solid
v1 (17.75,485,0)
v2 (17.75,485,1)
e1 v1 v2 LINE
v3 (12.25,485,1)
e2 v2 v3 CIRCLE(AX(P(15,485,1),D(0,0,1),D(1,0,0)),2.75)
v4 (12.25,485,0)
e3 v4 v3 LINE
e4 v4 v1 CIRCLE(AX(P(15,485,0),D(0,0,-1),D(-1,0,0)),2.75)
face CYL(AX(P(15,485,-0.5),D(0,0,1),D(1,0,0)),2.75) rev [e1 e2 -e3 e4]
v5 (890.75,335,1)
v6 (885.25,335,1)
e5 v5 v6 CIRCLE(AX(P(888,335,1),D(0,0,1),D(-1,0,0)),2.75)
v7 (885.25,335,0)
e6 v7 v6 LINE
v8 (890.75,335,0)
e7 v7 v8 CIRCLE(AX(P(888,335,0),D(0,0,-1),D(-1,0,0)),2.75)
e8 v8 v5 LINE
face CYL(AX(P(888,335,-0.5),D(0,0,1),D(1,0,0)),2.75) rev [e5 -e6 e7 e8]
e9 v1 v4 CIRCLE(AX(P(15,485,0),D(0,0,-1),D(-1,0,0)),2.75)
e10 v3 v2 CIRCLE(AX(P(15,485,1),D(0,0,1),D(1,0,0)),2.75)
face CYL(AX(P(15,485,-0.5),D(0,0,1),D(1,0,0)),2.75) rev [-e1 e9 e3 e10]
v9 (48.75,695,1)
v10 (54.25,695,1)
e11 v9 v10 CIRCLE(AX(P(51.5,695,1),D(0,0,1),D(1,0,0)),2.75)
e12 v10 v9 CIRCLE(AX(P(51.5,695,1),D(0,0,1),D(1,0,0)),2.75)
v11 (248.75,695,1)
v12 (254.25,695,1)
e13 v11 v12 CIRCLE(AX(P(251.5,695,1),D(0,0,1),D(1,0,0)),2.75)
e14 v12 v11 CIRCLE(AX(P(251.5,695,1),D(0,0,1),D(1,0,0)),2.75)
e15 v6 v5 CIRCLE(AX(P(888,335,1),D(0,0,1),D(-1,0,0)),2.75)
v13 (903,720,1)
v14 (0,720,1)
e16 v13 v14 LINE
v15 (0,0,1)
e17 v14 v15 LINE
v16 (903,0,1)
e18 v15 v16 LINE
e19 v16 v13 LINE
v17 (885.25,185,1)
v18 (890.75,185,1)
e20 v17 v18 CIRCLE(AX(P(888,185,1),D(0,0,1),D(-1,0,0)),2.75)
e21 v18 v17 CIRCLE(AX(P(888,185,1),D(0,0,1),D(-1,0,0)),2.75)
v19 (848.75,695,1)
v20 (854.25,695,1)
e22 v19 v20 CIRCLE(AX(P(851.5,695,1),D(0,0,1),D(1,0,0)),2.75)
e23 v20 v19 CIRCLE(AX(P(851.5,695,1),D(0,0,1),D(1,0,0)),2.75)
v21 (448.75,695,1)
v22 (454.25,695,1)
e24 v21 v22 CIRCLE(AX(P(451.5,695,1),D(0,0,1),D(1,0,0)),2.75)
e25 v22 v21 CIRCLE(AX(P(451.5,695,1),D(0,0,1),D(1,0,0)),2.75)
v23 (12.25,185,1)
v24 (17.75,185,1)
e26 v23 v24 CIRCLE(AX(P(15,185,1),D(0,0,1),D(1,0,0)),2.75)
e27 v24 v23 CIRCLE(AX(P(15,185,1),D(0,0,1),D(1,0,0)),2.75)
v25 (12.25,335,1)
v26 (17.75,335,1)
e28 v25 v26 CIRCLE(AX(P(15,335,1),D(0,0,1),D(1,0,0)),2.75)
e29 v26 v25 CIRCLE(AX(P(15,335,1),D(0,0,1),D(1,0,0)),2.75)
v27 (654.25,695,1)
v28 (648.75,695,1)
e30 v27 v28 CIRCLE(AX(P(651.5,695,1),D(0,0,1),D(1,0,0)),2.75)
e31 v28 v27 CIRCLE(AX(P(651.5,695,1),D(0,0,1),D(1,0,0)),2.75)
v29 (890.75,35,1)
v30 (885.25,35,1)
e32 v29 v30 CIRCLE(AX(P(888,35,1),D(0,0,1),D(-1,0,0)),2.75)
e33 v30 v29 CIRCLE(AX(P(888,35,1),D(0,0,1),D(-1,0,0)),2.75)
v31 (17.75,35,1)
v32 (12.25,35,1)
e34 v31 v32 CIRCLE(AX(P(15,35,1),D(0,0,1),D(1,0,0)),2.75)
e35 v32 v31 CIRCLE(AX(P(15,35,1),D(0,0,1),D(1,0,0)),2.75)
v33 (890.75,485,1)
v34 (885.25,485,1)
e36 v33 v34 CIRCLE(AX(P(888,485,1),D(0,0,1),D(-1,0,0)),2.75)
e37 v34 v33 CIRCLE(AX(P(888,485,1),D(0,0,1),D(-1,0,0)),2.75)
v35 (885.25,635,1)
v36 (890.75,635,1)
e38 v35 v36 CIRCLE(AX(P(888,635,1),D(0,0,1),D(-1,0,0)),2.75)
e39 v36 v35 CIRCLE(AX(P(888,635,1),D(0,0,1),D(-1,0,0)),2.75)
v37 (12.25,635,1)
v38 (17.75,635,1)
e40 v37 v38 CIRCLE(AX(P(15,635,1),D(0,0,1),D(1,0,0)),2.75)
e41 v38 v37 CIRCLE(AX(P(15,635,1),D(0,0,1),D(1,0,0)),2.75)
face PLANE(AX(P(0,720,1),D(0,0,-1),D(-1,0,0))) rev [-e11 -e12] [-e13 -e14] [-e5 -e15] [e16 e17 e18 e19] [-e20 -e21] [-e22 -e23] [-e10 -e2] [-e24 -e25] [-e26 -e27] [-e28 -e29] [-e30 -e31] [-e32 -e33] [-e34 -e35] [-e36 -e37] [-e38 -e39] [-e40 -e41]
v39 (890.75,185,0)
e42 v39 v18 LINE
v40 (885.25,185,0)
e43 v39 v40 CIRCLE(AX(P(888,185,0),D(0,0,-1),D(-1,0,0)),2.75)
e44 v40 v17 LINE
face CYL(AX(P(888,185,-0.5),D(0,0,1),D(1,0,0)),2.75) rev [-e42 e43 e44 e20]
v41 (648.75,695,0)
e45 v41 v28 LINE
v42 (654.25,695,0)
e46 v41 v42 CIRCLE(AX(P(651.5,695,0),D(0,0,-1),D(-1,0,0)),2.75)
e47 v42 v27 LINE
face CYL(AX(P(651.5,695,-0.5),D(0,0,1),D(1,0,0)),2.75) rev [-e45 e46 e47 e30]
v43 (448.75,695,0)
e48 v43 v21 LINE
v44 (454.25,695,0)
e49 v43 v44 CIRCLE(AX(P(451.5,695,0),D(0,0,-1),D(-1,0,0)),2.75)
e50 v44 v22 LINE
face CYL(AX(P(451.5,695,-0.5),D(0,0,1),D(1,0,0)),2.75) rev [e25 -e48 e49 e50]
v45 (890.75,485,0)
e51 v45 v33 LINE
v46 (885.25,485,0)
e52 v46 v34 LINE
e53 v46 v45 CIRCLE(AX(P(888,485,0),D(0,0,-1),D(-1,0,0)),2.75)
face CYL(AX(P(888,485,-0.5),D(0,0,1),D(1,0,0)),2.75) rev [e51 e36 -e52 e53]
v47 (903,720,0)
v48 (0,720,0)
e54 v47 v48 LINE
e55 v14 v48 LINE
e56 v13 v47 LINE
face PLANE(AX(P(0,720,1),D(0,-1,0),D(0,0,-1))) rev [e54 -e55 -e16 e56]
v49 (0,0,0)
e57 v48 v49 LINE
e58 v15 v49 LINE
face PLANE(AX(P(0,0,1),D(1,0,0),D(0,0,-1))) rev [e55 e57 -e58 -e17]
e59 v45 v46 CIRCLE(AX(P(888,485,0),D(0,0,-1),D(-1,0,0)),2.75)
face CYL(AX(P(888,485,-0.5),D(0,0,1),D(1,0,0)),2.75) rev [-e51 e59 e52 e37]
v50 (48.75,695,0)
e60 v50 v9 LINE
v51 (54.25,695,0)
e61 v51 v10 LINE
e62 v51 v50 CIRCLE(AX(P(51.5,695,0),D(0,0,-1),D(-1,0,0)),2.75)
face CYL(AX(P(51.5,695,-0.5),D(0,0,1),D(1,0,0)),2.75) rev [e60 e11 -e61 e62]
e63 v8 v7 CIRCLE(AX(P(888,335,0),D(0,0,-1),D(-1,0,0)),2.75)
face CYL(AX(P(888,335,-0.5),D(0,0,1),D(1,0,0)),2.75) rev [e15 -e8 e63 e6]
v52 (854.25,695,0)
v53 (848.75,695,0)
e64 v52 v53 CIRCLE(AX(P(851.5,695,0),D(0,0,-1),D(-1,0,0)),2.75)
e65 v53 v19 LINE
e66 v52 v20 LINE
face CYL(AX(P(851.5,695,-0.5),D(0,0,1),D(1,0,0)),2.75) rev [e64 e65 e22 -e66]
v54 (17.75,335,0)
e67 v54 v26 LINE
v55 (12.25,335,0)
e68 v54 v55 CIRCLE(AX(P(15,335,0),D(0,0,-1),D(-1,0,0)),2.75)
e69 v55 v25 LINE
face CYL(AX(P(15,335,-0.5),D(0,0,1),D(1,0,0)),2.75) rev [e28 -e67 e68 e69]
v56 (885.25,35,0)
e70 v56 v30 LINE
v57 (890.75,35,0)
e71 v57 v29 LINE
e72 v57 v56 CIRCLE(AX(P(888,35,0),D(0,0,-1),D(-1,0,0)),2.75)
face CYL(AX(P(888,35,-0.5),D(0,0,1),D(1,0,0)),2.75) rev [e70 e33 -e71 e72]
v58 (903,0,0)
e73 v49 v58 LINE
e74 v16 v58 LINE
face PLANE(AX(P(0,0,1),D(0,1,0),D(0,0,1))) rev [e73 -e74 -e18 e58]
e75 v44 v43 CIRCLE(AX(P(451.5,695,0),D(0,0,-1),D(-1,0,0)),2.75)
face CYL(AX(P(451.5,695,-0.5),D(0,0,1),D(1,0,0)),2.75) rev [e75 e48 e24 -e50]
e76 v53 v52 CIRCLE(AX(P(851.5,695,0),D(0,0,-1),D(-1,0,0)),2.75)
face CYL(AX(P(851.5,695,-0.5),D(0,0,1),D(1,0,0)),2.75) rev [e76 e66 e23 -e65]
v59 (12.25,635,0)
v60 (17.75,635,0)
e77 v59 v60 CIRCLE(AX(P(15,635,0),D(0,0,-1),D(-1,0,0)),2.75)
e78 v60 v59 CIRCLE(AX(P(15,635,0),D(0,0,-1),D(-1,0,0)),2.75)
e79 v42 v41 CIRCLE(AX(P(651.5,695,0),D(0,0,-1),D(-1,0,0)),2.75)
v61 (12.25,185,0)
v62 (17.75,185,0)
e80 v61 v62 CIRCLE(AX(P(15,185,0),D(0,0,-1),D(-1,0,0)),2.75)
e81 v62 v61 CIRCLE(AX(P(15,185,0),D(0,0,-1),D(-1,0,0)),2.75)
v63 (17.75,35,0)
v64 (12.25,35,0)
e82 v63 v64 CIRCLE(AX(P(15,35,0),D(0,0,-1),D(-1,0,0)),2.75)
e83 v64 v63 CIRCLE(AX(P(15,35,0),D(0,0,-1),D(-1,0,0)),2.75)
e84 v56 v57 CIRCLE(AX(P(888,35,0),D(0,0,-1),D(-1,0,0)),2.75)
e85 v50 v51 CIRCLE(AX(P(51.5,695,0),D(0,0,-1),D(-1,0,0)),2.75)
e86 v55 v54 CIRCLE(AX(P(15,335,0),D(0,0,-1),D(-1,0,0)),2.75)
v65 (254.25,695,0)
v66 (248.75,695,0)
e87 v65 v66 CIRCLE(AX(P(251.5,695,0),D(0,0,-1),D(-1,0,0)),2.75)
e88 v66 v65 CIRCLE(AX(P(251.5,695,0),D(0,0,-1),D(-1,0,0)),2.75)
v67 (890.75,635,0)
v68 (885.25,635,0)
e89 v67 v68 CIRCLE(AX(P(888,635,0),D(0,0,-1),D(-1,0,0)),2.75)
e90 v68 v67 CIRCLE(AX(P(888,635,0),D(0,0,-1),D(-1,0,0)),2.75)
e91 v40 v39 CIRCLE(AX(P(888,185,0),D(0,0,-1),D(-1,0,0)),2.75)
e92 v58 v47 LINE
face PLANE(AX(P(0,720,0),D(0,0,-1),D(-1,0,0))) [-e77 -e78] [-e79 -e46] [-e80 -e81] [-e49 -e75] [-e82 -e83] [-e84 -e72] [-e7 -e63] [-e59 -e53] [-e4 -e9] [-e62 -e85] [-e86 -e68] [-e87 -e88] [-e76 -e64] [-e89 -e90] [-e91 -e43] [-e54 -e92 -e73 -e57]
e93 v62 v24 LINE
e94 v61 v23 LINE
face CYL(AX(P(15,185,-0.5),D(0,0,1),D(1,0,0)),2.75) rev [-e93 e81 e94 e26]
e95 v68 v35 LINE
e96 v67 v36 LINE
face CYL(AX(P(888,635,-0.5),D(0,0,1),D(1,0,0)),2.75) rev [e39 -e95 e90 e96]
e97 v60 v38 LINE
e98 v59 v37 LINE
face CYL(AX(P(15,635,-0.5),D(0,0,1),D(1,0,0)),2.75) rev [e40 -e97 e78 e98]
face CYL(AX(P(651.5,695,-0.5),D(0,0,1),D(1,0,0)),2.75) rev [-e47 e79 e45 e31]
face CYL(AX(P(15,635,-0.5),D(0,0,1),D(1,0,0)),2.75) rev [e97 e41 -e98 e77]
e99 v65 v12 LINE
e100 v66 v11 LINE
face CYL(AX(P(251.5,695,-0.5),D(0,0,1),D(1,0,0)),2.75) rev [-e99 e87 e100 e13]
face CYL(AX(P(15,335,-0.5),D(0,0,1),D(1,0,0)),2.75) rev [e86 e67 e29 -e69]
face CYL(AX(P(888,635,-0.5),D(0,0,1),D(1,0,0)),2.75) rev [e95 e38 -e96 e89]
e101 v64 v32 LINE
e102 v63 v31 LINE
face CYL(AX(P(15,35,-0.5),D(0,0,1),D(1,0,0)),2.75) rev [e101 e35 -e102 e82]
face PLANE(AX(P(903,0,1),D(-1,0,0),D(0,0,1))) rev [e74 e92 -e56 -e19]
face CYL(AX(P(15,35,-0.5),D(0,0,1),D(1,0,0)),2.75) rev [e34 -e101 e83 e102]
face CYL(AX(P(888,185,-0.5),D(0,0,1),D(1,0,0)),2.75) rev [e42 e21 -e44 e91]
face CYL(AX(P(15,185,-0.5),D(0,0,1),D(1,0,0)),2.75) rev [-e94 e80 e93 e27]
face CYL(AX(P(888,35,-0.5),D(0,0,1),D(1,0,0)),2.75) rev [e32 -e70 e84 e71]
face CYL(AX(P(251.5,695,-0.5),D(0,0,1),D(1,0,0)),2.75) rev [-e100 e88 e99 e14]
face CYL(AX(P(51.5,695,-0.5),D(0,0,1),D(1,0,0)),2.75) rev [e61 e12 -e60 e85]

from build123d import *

# Parameters (mm, degrees)
SKETCH_1_W          = 903
SKETCH_1_H          = 720
EXTRUDE_1_DEPTH     = 1
SKETCH_2_R          = 2.75
CUT_EXTRUDE_1_DEPTH = 1.5


with BuildPart() as part:
    # 草图1 → 凸台-拉伸1 (new body)
    with BuildSketch(Plane.XY):
        with Locations((451.5, 360)):
            Rectangle(SKETCH_1_W, SKETCH_1_H)
    extrude(amount=EXTRUDE_1_DEPTH)

    # 草图2 → 切除-拉伸1 (cut)
    with BuildSketch(Plane.XY.offset(1)):
        with Locations((51.5, 695)):
            Circle(SKETCH_2_R)
        with Locations((15, 635)):
            Circle(SKETCH_2_R)
        with Locations((251.5, 695)):
            Circle(SKETCH_2_R)
        with Locations((451.5, 695)):
            Circle(SKETCH_2_R)
        with Locations((651.5, 695)):
            Circle(SKETCH_2_R)
        with Locations((851.5, 695)):
            Circle(SKETCH_2_R)
        with Locations((15, 485)):
            Circle(SKETCH_2_R)
        with Locations((15, 335)):
            Circle(SKETCH_2_R)
        with Locations((15, 185)):
            Circle(SKETCH_2_R)
        with Locations((15, 35)):
            Circle(SKETCH_2_R)
        with Locations(Location((888, 35, 0), (0, 0, 180))):
            Circle(SKETCH_2_R)
        with Locations(Location((888, 185, 0), (0, 0, 180))):
            Circle(SKETCH_2_R)
        with Locations(Location((888, 335, 0), (0, 0, 180))):
            Circle(SKETCH_2_R)
        with Locations(Location((888, 485, 0), (0, 0, 180))):
            Circle(SKETCH_2_R)
        with Locations(Location((888, 635, 0), (0, 0, 180))):
            Circle(SKETCH_2_R)
    extrude(amount=-CUT_EXTRUDE_1_DEPTH, mode=Mode.SUBTRACT)


solid = part.part
